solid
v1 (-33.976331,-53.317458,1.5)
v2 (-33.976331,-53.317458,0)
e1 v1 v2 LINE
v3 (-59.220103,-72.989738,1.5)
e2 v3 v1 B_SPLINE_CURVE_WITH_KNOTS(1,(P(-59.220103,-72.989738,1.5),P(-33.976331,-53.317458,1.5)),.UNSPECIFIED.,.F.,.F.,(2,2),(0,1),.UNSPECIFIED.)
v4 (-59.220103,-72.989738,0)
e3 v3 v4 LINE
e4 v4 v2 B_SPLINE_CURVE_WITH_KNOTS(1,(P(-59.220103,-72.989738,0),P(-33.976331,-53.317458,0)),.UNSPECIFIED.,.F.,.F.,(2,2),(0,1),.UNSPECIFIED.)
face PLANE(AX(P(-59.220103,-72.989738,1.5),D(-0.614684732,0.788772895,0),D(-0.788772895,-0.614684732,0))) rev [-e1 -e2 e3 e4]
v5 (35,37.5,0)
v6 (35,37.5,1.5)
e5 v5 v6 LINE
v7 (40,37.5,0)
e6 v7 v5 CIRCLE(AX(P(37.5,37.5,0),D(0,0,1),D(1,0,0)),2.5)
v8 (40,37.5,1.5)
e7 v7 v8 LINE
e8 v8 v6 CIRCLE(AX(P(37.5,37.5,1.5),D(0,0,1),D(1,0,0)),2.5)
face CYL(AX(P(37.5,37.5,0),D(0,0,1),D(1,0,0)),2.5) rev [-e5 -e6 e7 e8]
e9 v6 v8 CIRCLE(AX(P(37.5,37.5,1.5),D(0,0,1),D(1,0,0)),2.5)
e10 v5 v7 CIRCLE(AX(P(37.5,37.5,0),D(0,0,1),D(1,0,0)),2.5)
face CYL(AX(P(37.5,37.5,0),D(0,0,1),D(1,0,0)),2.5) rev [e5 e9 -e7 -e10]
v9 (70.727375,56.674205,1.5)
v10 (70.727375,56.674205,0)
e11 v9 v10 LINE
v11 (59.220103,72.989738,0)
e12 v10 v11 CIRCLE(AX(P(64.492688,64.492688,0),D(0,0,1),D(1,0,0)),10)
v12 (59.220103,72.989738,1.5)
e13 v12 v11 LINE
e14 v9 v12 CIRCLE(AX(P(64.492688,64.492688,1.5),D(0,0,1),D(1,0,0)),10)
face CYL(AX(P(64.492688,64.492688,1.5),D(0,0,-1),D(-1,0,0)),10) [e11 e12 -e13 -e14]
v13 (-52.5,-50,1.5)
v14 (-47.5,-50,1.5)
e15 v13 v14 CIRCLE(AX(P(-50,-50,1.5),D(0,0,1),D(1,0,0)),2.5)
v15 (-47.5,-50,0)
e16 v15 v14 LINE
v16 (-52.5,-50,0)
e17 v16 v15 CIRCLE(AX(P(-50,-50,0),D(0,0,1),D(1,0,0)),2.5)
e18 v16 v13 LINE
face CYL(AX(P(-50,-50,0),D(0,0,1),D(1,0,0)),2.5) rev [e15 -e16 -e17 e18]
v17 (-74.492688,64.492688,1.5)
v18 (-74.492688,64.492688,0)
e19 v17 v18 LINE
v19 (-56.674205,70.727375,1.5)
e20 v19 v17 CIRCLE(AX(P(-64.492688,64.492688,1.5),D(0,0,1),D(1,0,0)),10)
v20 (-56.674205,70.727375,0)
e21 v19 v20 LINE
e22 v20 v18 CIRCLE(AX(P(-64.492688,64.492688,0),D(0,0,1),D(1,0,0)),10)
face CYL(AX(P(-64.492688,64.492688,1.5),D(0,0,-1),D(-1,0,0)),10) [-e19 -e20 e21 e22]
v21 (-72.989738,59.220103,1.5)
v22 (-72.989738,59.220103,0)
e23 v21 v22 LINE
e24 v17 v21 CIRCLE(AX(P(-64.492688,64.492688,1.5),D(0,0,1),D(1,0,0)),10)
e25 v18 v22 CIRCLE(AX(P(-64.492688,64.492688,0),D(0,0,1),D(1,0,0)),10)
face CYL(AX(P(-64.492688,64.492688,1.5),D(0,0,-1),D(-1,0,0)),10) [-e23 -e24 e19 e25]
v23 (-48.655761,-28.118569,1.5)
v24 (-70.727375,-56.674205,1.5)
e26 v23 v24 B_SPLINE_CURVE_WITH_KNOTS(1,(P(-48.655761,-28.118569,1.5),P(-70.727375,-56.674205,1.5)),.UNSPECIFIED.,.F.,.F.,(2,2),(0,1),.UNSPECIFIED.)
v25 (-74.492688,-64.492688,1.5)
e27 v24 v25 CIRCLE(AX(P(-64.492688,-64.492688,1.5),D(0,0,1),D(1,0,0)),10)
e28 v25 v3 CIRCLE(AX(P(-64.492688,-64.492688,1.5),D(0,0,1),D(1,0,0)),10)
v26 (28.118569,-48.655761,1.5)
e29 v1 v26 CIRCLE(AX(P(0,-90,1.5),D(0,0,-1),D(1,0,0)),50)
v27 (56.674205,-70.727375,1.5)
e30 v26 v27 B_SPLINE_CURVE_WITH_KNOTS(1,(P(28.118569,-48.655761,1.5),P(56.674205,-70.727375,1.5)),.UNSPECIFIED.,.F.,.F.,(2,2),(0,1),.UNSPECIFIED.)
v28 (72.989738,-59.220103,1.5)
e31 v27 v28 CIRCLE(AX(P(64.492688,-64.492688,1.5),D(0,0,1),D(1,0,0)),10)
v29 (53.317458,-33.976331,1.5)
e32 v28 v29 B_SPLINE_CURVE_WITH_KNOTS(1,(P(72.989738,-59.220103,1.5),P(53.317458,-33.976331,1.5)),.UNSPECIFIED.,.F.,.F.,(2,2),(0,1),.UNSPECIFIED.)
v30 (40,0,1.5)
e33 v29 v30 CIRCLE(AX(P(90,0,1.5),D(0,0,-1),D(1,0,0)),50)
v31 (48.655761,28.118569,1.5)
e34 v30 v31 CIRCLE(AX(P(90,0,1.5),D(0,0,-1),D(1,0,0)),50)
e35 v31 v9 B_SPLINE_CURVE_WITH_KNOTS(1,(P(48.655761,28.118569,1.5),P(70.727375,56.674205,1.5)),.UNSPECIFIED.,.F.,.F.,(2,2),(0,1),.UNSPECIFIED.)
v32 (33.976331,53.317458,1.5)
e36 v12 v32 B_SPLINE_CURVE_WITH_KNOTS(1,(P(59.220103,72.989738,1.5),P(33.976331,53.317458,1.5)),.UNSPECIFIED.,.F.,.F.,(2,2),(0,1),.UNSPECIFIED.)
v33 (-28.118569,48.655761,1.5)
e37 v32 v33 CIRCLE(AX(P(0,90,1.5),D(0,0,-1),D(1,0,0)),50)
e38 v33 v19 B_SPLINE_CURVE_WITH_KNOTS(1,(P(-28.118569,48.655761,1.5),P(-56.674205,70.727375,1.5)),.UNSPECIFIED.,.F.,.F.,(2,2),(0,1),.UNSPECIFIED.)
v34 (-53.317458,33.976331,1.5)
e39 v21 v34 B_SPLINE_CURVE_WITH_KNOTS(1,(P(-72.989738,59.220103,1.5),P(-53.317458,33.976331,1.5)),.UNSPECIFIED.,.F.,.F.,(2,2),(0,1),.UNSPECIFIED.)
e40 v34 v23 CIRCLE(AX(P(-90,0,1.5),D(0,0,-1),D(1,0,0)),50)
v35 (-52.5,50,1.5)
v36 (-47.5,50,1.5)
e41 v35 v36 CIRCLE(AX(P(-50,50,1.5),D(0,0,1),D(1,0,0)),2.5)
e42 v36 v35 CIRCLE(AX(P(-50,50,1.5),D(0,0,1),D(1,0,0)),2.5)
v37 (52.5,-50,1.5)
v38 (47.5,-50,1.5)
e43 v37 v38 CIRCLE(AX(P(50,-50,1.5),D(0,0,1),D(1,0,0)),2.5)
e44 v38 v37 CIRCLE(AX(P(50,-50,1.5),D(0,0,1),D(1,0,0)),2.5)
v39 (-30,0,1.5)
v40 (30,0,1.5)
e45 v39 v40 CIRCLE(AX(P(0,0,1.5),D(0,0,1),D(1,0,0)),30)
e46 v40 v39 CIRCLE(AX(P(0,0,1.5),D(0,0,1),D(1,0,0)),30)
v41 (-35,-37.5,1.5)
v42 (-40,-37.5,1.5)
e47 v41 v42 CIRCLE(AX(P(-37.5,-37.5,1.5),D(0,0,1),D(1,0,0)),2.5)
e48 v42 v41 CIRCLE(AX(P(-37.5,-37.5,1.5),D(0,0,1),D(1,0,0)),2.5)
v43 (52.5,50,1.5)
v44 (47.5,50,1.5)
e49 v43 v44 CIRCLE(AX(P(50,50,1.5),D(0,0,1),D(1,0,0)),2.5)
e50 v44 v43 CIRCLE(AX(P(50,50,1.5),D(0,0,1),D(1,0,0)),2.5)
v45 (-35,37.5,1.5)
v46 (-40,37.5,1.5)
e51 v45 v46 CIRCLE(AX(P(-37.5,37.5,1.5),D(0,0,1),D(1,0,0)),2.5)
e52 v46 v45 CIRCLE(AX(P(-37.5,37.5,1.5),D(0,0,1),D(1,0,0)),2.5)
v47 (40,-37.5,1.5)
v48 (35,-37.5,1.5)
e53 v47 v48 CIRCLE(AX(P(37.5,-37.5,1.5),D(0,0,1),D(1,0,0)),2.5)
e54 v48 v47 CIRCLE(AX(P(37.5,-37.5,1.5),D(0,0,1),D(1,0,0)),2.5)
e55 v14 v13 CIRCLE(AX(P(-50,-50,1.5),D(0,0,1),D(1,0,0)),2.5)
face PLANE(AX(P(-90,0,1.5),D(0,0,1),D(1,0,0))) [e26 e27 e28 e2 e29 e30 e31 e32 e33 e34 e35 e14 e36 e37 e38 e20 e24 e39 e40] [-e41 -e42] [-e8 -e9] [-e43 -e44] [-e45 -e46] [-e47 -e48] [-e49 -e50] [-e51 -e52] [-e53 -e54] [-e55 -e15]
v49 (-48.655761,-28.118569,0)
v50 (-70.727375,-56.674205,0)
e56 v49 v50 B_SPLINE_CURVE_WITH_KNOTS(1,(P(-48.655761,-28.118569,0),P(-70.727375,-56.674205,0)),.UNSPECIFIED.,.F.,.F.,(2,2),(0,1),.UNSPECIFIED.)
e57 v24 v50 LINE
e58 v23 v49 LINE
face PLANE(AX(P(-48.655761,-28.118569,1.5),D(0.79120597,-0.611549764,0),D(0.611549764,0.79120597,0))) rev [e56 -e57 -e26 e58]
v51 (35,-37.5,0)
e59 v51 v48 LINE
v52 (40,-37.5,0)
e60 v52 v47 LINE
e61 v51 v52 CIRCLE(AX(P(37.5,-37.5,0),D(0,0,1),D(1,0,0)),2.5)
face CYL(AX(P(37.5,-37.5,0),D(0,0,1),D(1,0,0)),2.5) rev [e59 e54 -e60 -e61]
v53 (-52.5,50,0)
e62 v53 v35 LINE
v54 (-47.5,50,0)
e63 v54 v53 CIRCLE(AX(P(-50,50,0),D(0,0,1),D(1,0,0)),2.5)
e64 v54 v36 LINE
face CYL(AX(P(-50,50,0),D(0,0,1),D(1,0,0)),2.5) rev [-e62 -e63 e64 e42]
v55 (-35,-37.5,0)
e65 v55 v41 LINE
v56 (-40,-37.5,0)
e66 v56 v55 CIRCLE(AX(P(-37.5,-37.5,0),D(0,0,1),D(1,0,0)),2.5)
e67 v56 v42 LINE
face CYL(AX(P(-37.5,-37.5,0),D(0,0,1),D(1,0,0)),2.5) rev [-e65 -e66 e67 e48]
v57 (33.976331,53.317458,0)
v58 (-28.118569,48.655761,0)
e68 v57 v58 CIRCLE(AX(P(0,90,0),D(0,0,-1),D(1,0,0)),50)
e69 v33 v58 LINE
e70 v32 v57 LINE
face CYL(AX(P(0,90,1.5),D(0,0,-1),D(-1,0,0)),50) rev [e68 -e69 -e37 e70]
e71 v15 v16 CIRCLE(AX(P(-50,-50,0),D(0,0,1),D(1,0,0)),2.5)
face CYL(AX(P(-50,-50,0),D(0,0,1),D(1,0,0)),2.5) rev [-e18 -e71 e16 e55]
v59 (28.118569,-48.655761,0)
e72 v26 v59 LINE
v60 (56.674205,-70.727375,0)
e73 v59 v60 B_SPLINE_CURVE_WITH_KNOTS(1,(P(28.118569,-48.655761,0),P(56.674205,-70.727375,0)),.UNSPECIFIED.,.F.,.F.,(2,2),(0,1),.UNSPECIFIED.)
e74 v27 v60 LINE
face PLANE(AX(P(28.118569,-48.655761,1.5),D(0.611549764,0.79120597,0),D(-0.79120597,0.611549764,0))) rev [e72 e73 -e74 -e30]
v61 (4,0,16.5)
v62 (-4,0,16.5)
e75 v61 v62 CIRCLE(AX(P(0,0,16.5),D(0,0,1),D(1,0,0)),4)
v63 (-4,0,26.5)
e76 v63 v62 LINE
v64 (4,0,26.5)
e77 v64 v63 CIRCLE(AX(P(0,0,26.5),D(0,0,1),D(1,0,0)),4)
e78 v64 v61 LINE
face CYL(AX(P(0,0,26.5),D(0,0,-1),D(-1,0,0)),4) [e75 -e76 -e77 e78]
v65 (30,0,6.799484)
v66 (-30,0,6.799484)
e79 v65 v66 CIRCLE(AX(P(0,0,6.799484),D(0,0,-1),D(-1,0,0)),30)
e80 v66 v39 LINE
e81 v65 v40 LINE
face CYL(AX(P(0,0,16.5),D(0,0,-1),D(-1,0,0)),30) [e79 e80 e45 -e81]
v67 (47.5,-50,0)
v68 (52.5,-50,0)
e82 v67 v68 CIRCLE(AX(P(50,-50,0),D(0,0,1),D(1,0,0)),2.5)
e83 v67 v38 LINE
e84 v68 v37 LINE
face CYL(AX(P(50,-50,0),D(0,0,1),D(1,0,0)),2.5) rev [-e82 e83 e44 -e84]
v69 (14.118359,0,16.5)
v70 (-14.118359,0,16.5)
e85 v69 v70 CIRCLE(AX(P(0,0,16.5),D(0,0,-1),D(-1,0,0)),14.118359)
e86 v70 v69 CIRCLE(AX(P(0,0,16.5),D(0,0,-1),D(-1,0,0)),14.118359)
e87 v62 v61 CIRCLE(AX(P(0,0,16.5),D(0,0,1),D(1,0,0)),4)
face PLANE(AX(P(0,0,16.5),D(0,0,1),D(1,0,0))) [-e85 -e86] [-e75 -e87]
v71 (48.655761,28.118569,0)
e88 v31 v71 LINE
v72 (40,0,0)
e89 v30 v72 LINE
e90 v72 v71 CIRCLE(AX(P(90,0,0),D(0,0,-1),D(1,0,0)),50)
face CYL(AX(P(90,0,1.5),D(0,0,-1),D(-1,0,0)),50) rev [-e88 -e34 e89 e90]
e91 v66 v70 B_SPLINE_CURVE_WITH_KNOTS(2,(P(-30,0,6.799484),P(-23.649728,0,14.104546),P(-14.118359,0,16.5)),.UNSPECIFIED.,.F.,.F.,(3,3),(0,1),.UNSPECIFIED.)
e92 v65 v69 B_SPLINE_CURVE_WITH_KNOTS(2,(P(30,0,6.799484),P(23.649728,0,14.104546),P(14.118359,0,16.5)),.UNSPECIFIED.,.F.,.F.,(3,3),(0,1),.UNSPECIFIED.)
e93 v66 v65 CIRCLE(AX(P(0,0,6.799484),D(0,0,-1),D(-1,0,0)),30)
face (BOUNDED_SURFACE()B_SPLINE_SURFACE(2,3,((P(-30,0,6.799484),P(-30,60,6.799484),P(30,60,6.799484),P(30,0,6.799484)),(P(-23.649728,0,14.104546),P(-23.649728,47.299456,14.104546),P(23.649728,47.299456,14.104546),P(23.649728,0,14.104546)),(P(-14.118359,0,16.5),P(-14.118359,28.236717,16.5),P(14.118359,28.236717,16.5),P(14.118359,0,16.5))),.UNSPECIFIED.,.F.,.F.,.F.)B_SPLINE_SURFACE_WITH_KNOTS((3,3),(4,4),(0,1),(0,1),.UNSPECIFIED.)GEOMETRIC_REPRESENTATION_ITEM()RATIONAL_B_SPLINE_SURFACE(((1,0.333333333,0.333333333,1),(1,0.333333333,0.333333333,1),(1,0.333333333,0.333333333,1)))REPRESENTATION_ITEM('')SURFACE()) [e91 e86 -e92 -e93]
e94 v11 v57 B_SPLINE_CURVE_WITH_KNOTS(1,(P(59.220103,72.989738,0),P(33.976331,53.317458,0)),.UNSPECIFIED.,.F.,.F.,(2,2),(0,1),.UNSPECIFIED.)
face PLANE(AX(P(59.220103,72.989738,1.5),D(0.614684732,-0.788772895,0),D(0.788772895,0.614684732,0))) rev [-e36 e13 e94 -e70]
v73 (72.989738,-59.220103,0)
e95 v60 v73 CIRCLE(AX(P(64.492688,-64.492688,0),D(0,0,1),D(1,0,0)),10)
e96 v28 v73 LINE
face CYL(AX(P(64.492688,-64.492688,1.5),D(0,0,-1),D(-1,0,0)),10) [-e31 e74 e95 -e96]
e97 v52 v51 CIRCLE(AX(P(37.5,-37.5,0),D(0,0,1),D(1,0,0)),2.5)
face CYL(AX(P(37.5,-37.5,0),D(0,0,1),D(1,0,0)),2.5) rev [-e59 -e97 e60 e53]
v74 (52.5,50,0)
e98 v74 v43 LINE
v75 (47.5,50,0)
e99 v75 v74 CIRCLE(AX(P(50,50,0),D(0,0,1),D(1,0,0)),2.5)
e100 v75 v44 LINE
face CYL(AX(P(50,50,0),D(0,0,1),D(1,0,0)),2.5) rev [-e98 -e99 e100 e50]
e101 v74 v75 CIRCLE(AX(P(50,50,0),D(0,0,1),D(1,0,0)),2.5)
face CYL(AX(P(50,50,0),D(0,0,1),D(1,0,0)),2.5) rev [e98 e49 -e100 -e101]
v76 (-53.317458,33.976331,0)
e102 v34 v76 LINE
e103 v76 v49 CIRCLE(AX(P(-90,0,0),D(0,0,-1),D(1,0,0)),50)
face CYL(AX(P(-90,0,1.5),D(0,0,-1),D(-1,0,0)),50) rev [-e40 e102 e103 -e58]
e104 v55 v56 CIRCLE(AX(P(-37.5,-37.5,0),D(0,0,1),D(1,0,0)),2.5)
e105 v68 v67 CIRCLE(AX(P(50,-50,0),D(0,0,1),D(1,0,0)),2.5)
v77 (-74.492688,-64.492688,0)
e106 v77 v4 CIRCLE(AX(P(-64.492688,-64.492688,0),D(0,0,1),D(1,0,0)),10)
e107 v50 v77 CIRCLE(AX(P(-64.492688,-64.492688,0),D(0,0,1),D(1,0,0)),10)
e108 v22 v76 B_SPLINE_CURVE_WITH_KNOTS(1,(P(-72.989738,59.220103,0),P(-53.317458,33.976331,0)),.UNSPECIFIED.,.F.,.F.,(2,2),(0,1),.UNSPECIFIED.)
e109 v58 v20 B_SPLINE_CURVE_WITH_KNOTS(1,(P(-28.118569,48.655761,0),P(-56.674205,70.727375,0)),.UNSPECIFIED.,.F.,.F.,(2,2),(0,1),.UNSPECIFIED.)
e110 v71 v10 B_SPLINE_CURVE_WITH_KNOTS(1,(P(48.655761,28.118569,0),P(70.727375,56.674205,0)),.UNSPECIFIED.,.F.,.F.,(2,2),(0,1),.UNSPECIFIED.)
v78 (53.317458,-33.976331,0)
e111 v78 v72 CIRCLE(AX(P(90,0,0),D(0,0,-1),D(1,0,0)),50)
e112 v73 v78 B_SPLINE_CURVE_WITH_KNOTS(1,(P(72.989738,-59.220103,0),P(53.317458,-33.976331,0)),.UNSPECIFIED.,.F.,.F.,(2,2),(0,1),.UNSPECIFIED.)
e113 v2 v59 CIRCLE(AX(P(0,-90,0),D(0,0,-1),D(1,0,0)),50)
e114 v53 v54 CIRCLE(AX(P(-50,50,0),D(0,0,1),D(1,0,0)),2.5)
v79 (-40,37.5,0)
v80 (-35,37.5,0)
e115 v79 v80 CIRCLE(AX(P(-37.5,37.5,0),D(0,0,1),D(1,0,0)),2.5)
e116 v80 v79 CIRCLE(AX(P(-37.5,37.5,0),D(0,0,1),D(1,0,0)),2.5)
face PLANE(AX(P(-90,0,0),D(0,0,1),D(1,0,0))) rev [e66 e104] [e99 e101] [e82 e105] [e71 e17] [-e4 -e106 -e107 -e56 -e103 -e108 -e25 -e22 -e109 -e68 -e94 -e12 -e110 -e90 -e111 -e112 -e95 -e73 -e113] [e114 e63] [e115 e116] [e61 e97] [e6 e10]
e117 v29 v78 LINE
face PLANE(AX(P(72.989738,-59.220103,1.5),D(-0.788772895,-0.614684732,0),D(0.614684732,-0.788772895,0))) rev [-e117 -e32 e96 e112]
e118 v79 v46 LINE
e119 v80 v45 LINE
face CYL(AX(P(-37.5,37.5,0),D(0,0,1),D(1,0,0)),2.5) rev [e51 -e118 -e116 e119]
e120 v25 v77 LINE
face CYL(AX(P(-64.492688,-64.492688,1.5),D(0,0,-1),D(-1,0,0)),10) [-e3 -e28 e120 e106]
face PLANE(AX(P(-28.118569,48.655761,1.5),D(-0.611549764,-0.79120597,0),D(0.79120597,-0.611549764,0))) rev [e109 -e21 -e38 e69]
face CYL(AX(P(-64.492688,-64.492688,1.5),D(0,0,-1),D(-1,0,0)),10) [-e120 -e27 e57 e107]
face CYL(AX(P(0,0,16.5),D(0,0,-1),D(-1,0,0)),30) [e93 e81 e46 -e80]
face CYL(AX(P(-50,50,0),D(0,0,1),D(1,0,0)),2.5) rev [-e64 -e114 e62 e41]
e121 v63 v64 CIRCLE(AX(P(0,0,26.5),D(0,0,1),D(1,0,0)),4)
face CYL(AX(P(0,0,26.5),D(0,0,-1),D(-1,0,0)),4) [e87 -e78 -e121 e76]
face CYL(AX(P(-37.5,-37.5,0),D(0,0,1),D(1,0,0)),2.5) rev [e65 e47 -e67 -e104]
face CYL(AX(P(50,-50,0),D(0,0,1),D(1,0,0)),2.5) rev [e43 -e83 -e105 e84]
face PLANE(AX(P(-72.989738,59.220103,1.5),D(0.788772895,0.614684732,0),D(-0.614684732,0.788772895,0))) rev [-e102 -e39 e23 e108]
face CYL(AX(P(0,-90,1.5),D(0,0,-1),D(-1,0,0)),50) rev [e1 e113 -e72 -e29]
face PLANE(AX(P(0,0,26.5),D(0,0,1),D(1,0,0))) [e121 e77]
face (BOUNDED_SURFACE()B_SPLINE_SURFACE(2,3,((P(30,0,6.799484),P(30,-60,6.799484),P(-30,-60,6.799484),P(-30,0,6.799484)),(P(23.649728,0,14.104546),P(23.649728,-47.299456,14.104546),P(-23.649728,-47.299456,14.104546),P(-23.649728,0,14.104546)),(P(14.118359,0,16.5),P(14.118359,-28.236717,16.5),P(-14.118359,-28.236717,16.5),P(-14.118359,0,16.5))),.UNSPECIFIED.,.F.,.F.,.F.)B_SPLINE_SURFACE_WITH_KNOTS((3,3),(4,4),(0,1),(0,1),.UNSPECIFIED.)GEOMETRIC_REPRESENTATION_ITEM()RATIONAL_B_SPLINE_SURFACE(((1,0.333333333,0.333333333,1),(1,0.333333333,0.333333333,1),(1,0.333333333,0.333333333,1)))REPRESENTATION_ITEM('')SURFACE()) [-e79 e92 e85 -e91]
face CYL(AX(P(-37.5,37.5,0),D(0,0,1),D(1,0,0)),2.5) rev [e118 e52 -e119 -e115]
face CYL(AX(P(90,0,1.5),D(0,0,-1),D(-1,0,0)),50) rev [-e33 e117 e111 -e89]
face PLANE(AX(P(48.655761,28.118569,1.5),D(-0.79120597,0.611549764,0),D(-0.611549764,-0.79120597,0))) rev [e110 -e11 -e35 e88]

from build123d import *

# Parameters (mm, degrees)
EXTRUDE_1_DEPTH     = 1.5
SKETCH_4_R          = 2.5
CUT_EXTRUDE_1_DEPTH = 1.5
SKETCH_5_R          = 30
EXTRUDE_2_DEPTH     = 15
SKETCH_10_R         = 4
EXTRUDE_3_DEPTH     = 10


with BuildPart() as part:
    # 草图1 → 凸台-拉伸1 (new body)
    with BuildSketch(Plane.XY):
        with BuildLine():
            ThreePointArc((-28.118568833, 48.655761142), (-14.710337472, 42.212909992), (0, 40))
            ThreePointArc((0, 40), (18.246546062, 43.448270099), (33.976331356, 53.317457727))
            Line((33.976331356, 53.317457727), (59.220103302, 72.989737675))
            ThreePointArc((59.220103302, 72.989737675), (72.664625967, 70.256318884), (70.727374666, 56.674204713))
            Line((70.727374666, 56.674204713), (48.655761142, 28.118568833))
            ThreePointArc((48.655761142, 28.118568833), (42.212909992, 14.710337472), (40, 0))
            ThreePointArc((40, 0), (43.448270099, -18.246546062), (53.317457727, -33.976331356))
            Line((53.317457727, -33.976331356), (72.989737675, -59.220103302))
            ThreePointArc((72.989737675, -59.220103302), (70.256318884, -72.664625967), (56.674204713, -70.727374666))
            Line((56.674204713, -70.727374666), (28.118568833, -48.655761142))
            ThreePointArc((28.118568833, -48.655761142), (14.710337472, -42.212909992), (0, -40))
            ThreePointArc((0, -40), (-18.246546062, -43.448270099), (-33.976331356, -53.317457727))
            Line((-33.976331356, -53.317457727), (-59.220103302, -72.989737675))
            ThreePointArc((-59.220103302, -72.989737675), (-72.664625967, -70.256318884), (-70.727374666, -56.674204713))
            Line((-70.727374666, -56.674204713), (-48.655761142, -28.118568833))
            ThreePointArc((-48.655761142, -28.118568833), (-42.212909992, -14.710337472), (-40, 0))
            ThreePointArc((-40, 0), (-43.448270099, 18.246546062), (-53.317457727, 33.976331356))
            Line((-53.317457727, 33.976331356), (-72.989737675, 59.220103302))
            ThreePointArc((-72.989737675, 59.220103302), (-70.256318884, 72.664625967), (-56.674204713, 70.727374666))
            Line((-56.674204713, 70.727374666), (-28.118568833, 48.655761142))
        make_face()
    extrude(amount=EXTRUDE_1_DEPTH)

    # 草图4 → 切除-拉伸1 (cut)
    with BuildSketch(Plane.XY.offset(1.5)):
        with Locations((-50, 50)):
            Circle(SKETCH_4_R)
        with Locations((-37.5, 37.5)):
            Circle(SKETCH_4_R)
        with Locations((50, 50)):
            Circle(SKETCH_4_R)
        with Locations((37.5, 37.5)):
            Circle(SKETCH_4_R)
        with Locations((50, -50)):
            Circle(SKETCH_4_R)
        with Locations((37.5, -37.5)):
            Circle(SKETCH_4_R)
        with Locations((-50, -50)):
            Circle(SKETCH_4_R)
        with Locations((-37.5, -37.5)):
            Circle(SKETCH_4_R)
    extrude(amount=-CUT_EXTRUDE_1_DEPTH, mode=Mode.SUBTRACT)

    # 草图5 → 凸台-拉伸2 (add)
    with BuildSketch(Plane.XY.offset(1.5)):
        Circle(SKETCH_5_R)
    extrude(amount=EXTRUDE_2_DEPTH)

    # 草图6 → 切除-旋转1 (revolve, cut)
    with BuildSketch(Plane(origin=(0, 0, 0), x_dir=(1, 0, 0), z_dir=(0, 1, 0)), mode=Mode.PRIVATE) as cut_revolve_1_sk:
        with BuildLine():
            Line((30, -16.5), (30, -6.799483709))
            add(Edge.make_bspline(
                [(30, -6.799483709), (23.649728085, -14.104545992), (14.118358568, -16.5)],
                knots=[0, 0, 0, 1, 1, 1], degree=2))
            Line((14.118358568, -16.5), (30, -16.5))
        make_face()
    revolve(cut_revolve_1_sk.sketch.rotate(Axis((0, 0, 0), (0, 0, 1)), 180), axis=Axis((0, 0, 0), (0, 0, 1)), mode=Mode.SUBTRACT)

    # 草图10 → 凸台-拉伸3 (add)
    with BuildSketch(Plane.XY.offset(16.5)):
        Circle(SKETCH_10_R)
    extrude(amount=EXTRUDE_3_DEPTH)


solid = part.part
